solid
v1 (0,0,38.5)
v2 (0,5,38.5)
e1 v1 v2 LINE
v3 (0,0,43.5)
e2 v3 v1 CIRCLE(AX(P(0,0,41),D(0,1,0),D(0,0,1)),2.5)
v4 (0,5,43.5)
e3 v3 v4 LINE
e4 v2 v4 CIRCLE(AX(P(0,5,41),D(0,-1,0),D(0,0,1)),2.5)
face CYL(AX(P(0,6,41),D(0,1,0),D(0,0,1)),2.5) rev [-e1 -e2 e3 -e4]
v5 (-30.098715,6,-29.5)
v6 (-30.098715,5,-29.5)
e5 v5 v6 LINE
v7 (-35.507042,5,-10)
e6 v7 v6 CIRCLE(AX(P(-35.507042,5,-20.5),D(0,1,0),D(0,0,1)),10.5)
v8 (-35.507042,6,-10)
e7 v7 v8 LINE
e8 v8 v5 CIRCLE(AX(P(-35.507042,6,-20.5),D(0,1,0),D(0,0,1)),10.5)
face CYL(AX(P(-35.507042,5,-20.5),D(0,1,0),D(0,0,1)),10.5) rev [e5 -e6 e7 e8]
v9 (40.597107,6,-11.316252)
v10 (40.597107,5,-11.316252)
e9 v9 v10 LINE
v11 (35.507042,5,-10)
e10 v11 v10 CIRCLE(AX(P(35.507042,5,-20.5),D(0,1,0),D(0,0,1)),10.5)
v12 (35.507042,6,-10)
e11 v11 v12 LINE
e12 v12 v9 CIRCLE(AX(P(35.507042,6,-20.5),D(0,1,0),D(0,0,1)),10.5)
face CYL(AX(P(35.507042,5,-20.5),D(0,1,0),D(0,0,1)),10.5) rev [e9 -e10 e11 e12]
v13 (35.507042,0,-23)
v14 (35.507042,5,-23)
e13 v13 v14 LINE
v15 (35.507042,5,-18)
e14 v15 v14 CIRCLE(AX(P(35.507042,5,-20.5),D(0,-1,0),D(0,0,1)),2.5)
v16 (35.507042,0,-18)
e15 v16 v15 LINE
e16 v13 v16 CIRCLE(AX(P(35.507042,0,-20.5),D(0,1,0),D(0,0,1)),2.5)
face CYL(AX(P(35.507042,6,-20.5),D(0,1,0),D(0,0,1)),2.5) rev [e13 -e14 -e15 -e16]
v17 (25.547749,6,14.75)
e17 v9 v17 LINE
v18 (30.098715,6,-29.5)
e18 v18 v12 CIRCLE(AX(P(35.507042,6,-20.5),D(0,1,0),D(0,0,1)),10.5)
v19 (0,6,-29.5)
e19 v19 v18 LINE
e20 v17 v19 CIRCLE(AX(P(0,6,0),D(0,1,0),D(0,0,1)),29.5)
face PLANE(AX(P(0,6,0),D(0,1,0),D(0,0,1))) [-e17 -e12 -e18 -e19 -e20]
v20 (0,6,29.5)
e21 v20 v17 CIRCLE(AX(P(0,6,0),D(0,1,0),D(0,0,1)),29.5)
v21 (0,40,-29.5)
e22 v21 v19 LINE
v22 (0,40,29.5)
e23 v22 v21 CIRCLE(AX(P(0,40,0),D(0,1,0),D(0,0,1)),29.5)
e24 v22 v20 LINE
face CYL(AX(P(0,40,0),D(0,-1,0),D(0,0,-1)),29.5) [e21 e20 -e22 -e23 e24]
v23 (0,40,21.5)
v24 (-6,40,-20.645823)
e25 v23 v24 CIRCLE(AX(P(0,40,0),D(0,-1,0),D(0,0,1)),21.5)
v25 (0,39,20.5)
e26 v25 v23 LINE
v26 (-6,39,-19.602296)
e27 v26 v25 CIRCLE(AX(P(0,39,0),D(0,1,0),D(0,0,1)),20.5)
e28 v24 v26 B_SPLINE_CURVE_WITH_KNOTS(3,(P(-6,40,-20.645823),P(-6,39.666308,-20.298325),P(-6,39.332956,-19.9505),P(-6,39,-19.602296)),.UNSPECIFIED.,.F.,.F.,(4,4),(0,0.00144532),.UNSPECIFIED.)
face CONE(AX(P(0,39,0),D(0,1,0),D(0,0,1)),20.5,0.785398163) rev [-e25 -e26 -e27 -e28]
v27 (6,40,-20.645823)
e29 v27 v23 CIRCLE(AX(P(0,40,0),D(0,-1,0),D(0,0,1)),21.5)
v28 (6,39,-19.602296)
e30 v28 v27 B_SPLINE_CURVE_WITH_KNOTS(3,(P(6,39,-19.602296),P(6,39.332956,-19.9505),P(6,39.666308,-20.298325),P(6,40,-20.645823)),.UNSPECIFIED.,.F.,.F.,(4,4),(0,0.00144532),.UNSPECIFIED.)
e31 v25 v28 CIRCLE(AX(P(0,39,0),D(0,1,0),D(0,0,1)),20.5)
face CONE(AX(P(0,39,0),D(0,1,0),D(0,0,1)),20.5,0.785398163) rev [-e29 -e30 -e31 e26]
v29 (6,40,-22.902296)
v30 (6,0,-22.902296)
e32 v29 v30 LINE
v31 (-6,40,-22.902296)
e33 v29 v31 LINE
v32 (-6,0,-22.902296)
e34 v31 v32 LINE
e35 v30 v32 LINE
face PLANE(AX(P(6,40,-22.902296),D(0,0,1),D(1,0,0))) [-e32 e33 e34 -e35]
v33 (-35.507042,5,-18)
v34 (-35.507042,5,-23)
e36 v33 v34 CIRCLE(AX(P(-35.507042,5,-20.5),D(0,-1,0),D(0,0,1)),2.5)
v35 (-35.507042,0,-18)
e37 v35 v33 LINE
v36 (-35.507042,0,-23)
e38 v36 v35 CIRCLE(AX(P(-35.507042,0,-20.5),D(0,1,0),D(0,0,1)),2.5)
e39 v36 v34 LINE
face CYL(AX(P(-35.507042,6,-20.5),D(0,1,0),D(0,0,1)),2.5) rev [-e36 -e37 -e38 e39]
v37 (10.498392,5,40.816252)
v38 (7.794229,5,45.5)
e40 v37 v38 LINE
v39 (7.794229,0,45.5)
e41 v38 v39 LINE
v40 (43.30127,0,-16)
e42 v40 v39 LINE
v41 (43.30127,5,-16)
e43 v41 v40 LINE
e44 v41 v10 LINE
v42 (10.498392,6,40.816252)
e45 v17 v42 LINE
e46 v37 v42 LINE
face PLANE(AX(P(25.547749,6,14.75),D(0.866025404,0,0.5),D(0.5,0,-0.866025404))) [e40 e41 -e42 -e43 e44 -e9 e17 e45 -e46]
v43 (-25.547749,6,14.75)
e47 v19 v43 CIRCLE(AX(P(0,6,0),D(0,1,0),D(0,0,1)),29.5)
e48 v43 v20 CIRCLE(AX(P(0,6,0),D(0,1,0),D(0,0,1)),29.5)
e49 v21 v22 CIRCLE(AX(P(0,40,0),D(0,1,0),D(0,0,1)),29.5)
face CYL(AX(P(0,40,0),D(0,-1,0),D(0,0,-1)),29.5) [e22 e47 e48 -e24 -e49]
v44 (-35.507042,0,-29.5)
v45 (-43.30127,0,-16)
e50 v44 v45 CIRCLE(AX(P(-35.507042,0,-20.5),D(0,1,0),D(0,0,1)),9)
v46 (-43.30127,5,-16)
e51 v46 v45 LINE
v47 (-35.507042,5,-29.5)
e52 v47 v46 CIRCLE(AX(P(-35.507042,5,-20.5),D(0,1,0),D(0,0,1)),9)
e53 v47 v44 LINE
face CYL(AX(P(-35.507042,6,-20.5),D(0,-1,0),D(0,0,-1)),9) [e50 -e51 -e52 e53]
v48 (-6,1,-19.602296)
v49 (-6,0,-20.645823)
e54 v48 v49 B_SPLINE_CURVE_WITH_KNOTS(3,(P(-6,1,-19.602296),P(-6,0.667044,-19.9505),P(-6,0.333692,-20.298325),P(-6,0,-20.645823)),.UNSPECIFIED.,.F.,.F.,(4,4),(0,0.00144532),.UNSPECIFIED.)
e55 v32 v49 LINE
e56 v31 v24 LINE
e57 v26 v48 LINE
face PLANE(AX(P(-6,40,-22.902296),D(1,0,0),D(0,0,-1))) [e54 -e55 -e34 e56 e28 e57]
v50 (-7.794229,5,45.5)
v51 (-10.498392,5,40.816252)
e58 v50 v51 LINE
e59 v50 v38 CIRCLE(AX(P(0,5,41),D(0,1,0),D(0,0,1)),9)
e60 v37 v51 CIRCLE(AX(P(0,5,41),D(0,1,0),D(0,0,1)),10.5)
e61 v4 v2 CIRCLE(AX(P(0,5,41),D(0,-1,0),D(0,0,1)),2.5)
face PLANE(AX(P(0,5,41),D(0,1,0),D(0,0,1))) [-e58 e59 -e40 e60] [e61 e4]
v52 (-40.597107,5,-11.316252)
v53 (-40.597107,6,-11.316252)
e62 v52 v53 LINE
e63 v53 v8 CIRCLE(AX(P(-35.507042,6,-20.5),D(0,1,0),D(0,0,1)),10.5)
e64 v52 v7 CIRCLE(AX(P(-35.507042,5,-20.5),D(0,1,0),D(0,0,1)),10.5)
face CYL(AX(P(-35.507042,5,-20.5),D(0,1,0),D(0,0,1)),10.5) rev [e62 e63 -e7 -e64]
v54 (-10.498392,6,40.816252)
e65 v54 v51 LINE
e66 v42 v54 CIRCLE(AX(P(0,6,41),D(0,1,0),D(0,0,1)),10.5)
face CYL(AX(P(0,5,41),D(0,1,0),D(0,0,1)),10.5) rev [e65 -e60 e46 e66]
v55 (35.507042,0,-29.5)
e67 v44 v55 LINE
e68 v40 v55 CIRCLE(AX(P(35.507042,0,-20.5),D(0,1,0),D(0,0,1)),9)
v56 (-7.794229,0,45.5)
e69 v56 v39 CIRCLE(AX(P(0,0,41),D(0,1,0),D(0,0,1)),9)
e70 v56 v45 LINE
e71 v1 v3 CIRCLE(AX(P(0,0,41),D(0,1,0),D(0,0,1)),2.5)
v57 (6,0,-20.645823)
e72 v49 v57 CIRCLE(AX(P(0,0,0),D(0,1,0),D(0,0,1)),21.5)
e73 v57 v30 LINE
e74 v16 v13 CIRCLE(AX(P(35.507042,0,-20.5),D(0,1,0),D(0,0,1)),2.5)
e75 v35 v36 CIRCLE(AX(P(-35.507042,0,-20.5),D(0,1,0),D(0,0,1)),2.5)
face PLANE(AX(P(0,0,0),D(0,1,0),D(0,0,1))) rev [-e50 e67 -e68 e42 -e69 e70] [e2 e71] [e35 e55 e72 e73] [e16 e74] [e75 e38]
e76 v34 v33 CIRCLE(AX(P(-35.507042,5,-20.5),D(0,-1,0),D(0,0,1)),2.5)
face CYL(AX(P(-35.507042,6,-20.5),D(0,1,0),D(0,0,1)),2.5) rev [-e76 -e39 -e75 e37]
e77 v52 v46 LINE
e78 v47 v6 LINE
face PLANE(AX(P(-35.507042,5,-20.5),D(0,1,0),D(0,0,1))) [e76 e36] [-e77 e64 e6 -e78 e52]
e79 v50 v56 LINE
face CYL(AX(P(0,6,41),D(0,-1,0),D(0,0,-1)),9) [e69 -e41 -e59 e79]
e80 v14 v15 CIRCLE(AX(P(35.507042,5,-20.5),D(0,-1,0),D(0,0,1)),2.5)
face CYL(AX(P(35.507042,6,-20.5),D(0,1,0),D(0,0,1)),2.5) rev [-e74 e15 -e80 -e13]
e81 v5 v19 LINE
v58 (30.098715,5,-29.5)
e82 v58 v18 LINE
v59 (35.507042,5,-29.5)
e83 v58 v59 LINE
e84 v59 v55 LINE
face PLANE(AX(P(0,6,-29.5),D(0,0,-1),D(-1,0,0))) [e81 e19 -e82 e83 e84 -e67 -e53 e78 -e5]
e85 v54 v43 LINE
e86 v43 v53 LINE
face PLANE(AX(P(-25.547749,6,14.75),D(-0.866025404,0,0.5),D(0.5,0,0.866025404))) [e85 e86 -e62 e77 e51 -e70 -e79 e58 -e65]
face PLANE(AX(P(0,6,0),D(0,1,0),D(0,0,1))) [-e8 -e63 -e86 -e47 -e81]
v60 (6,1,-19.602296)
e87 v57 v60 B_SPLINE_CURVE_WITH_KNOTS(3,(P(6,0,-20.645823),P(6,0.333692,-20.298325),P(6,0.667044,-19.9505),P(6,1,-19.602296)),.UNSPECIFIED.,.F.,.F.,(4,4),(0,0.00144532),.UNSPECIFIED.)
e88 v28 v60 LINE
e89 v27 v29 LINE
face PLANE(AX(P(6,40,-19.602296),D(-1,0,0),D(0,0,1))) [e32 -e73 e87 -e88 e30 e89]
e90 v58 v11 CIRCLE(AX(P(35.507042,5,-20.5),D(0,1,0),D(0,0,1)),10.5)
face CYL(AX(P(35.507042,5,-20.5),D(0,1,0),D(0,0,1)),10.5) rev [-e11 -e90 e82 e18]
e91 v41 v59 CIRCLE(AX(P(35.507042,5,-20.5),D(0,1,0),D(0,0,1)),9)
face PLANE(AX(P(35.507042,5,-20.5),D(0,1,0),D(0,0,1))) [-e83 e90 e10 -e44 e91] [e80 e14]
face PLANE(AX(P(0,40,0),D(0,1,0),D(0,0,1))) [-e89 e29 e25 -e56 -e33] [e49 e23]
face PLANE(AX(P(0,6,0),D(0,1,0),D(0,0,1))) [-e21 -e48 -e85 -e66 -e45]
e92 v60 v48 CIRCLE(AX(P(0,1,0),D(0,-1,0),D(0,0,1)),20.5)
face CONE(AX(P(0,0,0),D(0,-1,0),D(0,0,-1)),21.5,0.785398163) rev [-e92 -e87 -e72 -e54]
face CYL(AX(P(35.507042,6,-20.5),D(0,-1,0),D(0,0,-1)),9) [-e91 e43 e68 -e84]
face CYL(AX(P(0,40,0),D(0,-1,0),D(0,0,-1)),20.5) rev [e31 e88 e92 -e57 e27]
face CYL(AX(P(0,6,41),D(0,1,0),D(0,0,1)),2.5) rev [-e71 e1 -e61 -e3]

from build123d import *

# Parameters (mm, degrees)
EXTRUDE_1_DEPTH        = 6
EXTRUDE_1_2_DEPTH      = 6
EXTRUDE_1_3_DEPTH      = 6
SKETCH_2_R             = 29.5
EXTRUDE_2_DEPTH        = 40
CHAMFER_1_SIZE         = 1
HOLE_WIZARD_M6_1_D     = 5
HOLE_WIZARD_M6_1_DEPTH = 15
HOLE_WIZARD_M6_1_TIP   = 1.502151548
SKETCH_5_R             = 10.5
CUT_EXTRUDE_1_DEPTH    = 1


with BuildPart() as part:
    # 草图1 → 凸台-拉伸1 (new body)
    with BuildSketch(Plane(origin=(0, 0, 0), x_dir=(1, 0, 0), z_dir=(0, 1, 0))):
        with BuildLine():
            Line((1.03e-07, 29.5), (-35.507041555, 29.5))
            ThreePointArc((-35.507041555, 29.5), (-43.301270189, 25), (-43.301270189, 16))
            Line((-43.301270189, 16), (-25.547749424, -14.749999978))
            ThreePointArc((-25.547749424, -14.749999978), (-25.54774938, 14.750000056), (1.03e-07, 29.5))
        make_face()
    extrude(amount=EXTRUDE_1_DEPTH)



with BuildPart() as body_2:
    # 草图1 → Extrude 1 2 (new body)
    with BuildSketch(Plane(origin=(0, 0, 0), x_dir=(1, 0, 0), z_dir=(0, 1, 0))):
        with BuildLine():
            ThreePointArc((25.547749421, -14.749999984), (-3e-09, -29.5), (-25.547749424, -14.749999978))
            Line((-25.547749424, -14.749999978), (-7.794228634, -45.5))
            ThreePointArc((-7.794228634, -45.5), (0, -50), (7.794228634, -45.5))
            Line((7.794228634, -45.5), (25.547749421, -14.749999984))
        make_face()
    extrude(amount=EXTRUDE_1_2_DEPTH)


with BuildPart() as body_3:
    # 草图1 → Extrude 1 3 (new body)
    with BuildSketch(Plane(origin=(0, 0, 0), x_dir=(1, 0, 0), z_dir=(0, 1, 0))):
        with BuildLine():
            Line((35.507041555, 29.5), (1.03e-07, 29.5))
            ThreePointArc((1.03e-07, 29.5), (20.859650082, 20.859650009), (29.5, 0))
            ThreePointArc((29.5, 0), (28.494811878, -7.635161822), (25.547749421, -14.749999984))
            Line((25.547749421, -14.749999984), (43.301270189, 16))
            ThreePointArc((43.301270189, 16), (43.301270189, 25), (35.507041555, 29.5))
        make_face()
    extrude(amount=EXTRUDE_1_3_DEPTH)


with BuildPart() as part_1:
    add(part.part)

    add(body_2.part)  # 凸台-拉伸2 merges body 2

    add(body_3.part)  # 凸台-拉伸2 merges body 3
    # 草图2 → 凸台-拉伸2 (add)
    with BuildSketch(Plane(origin=(0, 0, 0), x_dir=(1, 0, 0), z_dir=(0, 1, 0))):
        with Locations(Location((0, 0, 0), (0, 0, 90))):
            Circle(SKETCH_2_R)
        with BuildLine():
            Line((6, 19.602295784), (6, 22.902295784))
            Line((6, 22.902295784), (-6, 22.902295784))
            Line((-6, 22.902295784), (-6, 19.602295784))
            ThreePointArc((-6, 19.602295784), (0, -20.5), (6, 19.602295784))
        make_face(mode=Mode.SUBTRACT)
    extrude(amount=EXTRUDE_2_DEPTH)

    # 倒角1
    chamfer_1_edges = [part_1.edges().sort_by_distance(p)[0] for p in [
        (0, 0, 20.5),
        (0, 40, 20.5),
    ]]
    chamfer(chamfer_1_edges, length=CHAMFER_1_SIZE)

    # M6 螺纹孔1
    with Locations(Plane(origin=(0, 6, 0), x_dir=(1, 0, 0), z_dir=(0, 1, 0))):
        with Locations((-35.507041555, 20.5), (35.507041555, 20.5), (0, -41)):
            Hole(HOLE_WIZARD_M6_1_D / 2, depth=HOLE_WIZARD_M6_1_DEPTH)
            with Locations((0, 0, -(HOLE_WIZARD_M6_1_DEPTH + HOLE_WIZARD_M6_1_TIP / 2))):  # 118° drill point
                Cone(0, HOLE_WIZARD_M6_1_D / 2, HOLE_WIZARD_M6_1_TIP, mode=Mode.SUBTRACT)

    # 草图5 → 切除-拉伸1 (cut)
    with BuildSketch(Plane(origin=(0, 6, 0), x_dir=(1, 0, 0), z_dir=(0, 1, 0))):
        with Locations((-35.507041555, 20.5)):
            Circle(SKETCH_5_R)
        with Locations((35.507041555, 20.5)):
            Circle(SKETCH_5_R)
        with Locations((0, -41)):
            Circle(SKETCH_5_R)
    extrude(amount=-CUT_EXTRUDE_1_DEPTH, mode=Mode.SUBTRACT)


solid = part_1.part
